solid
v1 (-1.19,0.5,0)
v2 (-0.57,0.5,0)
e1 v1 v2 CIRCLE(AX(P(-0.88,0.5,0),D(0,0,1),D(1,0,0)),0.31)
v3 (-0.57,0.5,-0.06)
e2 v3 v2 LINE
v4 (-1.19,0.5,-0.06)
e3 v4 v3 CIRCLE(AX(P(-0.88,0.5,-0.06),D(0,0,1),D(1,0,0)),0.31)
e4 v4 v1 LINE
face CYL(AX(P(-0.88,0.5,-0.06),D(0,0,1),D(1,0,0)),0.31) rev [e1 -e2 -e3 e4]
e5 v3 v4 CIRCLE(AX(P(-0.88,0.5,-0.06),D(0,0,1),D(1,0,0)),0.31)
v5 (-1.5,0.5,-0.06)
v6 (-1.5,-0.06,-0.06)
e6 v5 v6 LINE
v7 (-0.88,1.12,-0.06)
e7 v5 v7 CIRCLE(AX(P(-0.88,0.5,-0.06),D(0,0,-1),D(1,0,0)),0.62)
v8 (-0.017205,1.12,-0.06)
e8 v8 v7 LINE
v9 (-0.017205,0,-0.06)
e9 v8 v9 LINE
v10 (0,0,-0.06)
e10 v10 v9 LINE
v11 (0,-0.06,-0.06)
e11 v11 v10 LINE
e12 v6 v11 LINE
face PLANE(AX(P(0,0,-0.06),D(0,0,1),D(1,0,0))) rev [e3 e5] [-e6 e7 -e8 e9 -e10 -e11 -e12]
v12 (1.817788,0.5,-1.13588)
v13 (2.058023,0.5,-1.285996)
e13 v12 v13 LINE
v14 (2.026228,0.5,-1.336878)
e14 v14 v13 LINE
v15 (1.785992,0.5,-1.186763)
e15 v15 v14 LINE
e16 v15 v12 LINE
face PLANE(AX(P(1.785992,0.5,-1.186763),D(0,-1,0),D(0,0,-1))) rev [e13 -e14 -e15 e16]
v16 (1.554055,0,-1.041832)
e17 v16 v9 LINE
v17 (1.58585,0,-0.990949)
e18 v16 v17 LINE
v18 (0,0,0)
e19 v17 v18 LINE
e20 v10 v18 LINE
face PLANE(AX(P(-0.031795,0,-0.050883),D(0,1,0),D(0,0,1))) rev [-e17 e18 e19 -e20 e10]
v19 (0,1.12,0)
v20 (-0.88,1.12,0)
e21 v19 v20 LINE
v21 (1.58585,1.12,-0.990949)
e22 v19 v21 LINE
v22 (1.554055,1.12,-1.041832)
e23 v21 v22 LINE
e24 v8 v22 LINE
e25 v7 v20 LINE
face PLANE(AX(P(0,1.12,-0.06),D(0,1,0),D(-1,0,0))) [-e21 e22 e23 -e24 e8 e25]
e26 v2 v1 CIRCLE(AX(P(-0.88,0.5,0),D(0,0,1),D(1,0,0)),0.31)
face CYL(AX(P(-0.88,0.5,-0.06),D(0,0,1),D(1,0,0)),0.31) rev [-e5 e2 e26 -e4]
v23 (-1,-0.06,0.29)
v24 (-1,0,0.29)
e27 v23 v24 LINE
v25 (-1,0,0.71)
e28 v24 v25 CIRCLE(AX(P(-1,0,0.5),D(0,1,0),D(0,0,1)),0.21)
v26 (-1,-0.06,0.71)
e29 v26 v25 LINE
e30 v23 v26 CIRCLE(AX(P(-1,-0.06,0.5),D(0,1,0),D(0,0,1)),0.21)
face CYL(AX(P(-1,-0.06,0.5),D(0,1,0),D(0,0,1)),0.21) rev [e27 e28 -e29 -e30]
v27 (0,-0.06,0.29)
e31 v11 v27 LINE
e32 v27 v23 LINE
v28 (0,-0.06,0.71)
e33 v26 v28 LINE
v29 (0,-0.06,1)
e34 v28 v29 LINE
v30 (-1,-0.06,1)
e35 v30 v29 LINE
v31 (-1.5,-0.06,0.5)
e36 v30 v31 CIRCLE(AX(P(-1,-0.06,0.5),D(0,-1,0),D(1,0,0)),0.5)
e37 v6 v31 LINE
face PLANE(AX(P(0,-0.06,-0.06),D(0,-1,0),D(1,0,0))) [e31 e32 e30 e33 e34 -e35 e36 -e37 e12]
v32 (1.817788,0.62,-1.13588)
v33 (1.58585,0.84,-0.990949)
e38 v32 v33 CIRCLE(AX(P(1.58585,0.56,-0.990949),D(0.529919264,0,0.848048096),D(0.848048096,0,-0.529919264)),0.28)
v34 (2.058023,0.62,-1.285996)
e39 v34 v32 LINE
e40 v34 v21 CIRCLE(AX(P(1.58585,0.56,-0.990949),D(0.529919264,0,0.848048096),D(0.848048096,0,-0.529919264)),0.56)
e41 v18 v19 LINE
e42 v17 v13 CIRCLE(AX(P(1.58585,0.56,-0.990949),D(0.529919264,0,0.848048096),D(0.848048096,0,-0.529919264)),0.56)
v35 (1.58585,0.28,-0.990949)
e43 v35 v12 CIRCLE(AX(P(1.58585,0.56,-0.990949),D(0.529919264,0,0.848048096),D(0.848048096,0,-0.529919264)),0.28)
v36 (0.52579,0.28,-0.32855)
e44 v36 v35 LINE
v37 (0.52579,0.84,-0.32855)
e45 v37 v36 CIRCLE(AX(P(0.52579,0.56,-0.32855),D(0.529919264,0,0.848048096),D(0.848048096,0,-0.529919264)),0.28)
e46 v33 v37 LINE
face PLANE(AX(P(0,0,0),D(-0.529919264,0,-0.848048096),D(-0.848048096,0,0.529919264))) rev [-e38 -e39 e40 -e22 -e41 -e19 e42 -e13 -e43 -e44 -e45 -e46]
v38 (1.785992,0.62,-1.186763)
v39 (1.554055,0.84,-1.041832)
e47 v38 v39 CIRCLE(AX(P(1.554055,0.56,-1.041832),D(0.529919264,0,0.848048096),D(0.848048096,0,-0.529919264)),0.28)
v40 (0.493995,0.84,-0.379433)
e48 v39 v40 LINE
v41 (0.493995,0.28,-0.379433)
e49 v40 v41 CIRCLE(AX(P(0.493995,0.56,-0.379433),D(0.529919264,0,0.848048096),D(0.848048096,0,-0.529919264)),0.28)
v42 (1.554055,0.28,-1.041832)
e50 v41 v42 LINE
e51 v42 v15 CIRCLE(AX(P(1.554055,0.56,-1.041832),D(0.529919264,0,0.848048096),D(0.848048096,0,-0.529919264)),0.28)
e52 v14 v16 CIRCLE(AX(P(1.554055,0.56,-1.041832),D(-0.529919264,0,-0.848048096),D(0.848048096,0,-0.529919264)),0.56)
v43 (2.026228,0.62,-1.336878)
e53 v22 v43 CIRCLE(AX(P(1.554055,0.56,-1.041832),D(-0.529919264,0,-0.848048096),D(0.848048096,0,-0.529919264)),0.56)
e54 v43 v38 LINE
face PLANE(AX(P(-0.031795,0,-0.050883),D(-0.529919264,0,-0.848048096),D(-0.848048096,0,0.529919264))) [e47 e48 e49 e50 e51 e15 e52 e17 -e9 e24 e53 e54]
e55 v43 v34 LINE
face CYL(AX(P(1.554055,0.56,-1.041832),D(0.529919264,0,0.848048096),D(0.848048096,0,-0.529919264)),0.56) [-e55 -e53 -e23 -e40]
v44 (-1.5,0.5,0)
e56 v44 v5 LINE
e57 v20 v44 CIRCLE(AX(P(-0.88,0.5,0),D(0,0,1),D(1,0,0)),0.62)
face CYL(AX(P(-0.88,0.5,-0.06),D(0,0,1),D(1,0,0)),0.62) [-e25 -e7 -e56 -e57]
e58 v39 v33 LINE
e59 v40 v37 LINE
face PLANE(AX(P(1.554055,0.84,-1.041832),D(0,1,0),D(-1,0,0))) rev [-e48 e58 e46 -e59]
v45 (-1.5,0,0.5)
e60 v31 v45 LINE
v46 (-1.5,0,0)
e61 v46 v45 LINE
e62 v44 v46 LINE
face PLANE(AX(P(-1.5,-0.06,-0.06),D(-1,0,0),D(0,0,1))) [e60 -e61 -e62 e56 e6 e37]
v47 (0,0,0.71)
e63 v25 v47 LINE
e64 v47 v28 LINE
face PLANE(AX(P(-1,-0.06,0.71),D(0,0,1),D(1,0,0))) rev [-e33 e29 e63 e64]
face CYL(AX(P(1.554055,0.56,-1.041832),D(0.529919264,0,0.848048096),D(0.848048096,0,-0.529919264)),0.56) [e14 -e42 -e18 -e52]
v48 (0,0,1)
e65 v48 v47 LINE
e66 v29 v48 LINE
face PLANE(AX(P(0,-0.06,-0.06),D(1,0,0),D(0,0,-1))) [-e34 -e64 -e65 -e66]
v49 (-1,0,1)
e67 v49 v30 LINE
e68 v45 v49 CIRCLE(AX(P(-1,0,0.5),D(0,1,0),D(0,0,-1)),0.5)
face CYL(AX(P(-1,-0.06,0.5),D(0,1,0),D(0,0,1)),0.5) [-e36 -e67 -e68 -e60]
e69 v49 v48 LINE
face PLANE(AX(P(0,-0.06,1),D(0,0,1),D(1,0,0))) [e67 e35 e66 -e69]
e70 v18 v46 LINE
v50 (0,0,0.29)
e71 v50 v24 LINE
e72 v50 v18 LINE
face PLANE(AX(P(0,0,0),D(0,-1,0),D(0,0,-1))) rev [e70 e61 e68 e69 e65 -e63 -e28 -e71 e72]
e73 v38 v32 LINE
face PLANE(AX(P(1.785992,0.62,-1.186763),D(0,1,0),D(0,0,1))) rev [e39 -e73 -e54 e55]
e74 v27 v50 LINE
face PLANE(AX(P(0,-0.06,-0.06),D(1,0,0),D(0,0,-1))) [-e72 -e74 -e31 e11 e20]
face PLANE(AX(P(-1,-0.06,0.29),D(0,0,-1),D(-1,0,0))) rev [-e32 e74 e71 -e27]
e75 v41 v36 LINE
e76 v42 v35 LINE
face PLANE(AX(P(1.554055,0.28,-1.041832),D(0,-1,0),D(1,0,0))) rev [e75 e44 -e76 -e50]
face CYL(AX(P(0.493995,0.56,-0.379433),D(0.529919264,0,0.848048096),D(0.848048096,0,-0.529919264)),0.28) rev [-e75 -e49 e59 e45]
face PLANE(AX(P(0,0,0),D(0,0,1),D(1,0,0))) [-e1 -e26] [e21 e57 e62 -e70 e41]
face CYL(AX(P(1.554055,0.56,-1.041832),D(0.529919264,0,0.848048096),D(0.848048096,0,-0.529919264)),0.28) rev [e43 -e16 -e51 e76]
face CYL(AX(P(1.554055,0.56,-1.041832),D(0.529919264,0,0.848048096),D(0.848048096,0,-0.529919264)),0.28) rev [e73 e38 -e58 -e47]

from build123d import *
from OCP.BRepFilletAPI import BRepFilletAPI_MakeFillet

# Parameters (mm, degrees)
VERTICAL_TAB_SKETCH_W    = 1.5
VERTICAL_TAB_SKETCH_H    = 1.18
VERTICAL_TAB_DEPTH       = 0.06
FOOT_SKETCH_W            = 1.5
FOOT_SKETCH_H            = 1
FOOT_DEPTH               = 0.06
ARM_SKETCH_W             = 2.43
ARM_SKETCH_H             = 1.12
ANGLED_ARM_DEPTH         = 0.06
TAB_CORNER_ROUNDS_R1     = 0.62
TAB_CORNER_ROUNDS_R2     = 0.5
TAB_HOLE_SKETCH_R        = 0.31
TAB_HOLE_DEPTH           = 0.06
FOOT_OPEN_SLOT_DEPTH     = 0.06
ARM_END_ROUNDS_RADIUS    = 0.56
ARM_END_ROUNDS_LENGTH    = 0.06
ARM_SLOT_WITH_SLIT_DEPTH = 0.06


with BuildPart() as part:
    # Vertical Tab Sketch → Vertical Tab (new body)
    with BuildSketch(Plane.XY):
        with Locations((-0.75, 0.53)):
            Rectangle(VERTICAL_TAB_SKETCH_W, VERTICAL_TAB_SKETCH_H)
    extrude(amount=-VERTICAL_TAB_DEPTH)

    # Foot Sketch → Foot (add)
    with BuildSketch(Plane(origin=(0, 0, 0), x_dir=(1, 0, 0), z_dir=(0, 1, 0))):
        with Locations((-0.75, -0.5)):
            Rectangle(FOOT_SKETCH_W, FOOT_SKETCH_H)
    extrude(amount=-FOOT_DEPTH)

    # Arm Sketch → Angled Arm (add)
    with BuildSketch(Plane(origin=(0, 0, 0), x_dir=(0.8480480961564255, 0, -0.5299192642332059), z_dir=(-0.5299192642332058, 0, -0.8480480961564254))):
        with Locations((1.215, -0.56)):
            Rectangle(ARM_SKETCH_W, ARM_SKETCH_H)
    extrude(amount=ANGLED_ARM_DEPTH)

    # Tab Corner Rounds: one fillet with a radius per group of edges: ONE call of the kernel's fillet builder (fillet() takes one radius for all edges)
    tab_corner_rounds_edges_1 = [part.edges().sort_by_distance(p)[0] for p in [
        (-1.5, 1.12, -0.03),
    ]]
    tab_corner_rounds_edges_2 = [part.edges().sort_by_distance(p)[0] for p in [
        (-1.5, -0.03, 1),
    ]]
    tab_corner_rounds = BRepFilletAPI_MakeFillet(part.part.solid().wrapped)
    for e in tab_corner_rounds_edges_1:
        tab_corner_rounds.Add(TAB_CORNER_ROUNDS_R1, e.wrapped)
    for e in tab_corner_rounds_edges_2:
        tab_corner_rounds.Add(TAB_CORNER_ROUNDS_R2, e.wrapped)
    add(Compound.cast(tab_corner_rounds.Shape()), mode=Mode.REPLACE)

    # Tab Hole Sketch → Tab Hole (cut)
    with BuildSketch(Plane.XY):
        with Locations((-0.88, 0.5)):
            Circle(TAB_HOLE_SKETCH_R)
    extrude(amount=-TAB_HOLE_DEPTH, mode=Mode.SUBTRACT)

    # Foot Slot Sketch → Foot Open Slot (cut)
    with BuildSketch(Plane(origin=(0, 0, 0), x_dir=(1, 0, 0), z_dir=(0, 1, 0))):
        with BuildLine():
            Line((-1, -0.29), (0.146073604, -0.29))
            ThreePointArc((0.146073604, -0.29), (0.356073604, -0.5), (0.146073604, -0.71))
            Line((0.146073604, -0.71), (-1, -0.71))
            ThreePointArc((-1, -0.71), (-1.21, -0.5), (-1, -0.29))
        make_face()
    extrude(amount=-FOOT_OPEN_SLOT_DEPTH, mode=Mode.SUBTRACT)

    # Arm End Rounds: full round fillet: the end face becomes a half cylinder, R = half its width
    arm_end_rounds_face = Plane((2.044859296, 0.56, -1.313145255), x_dir=(0.529919264233, 0, 0.848048096156), z_dir=(0.848048096156, 0, -0.529919264233))  # on the end face: x along it, z out of the body
    arm_end_rounds_slab = arm_end_rounds_face.offset(-ARM_END_ROUNDS_RADIUS / 2) * Box(ARM_END_ROUNDS_LENGTH, 2 * ARM_END_ROUNDS_RADIUS, ARM_END_ROUNDS_RADIUS, mode=Mode.PRIVATE)  # the body's end, R deep
    arm_end_rounds_round = Plane((1.569952362, 0.56, -1.016390467), x_dir=(0.848048096156, 0, -0.529919264233), z_dir=(0.529919264233, 0, 0.848048096156)) * Cylinder(ARM_END_ROUNDS_RADIUS, ARM_END_ROUNDS_LENGTH, mode=Mode.PRIVATE)  # its axis R under the face
    add(arm_end_rounds_slab - arm_end_rounds_round, mode=Mode.SUBTRACT)

    # Arm Slot Sketch → Arm Slot with Slit (cut)
    with BuildSketch(Plane(origin=(0, 0, 0), x_dir=(0.8480480961564255, 0, -0.5299192642332059), z_dir=(0.5299192642332058, 0, 0.8480480961564254))):
        with BuildLine():
            Line((1.87, 0.28), (0.62, 0.28))
            ThreePointArc((0.62, 0.28), (0.34, 0.56), (0.62, 0.84))
            Line((0.62, 0.84), (1.87, 0.84))
            ThreePointArc((1.87, 0.84), (2.045499288, 0.778174242), (2.143495887, 0.62))
            Line((2.143495887, 0.62), (2.426776436, 0.62))
            Line((2.426776436, 0.62), (2.426776436, 0.5))
            Line((2.426776436, 0.5), (2.143495887, 0.5))
            ThreePointArc((2.143495887, 0.5), (2.045499288, 0.341825758), (1.87, 0.28))
        make_face()
    extrude(amount=-ARM_SLOT_WITH_SLIT_DEPTH, mode=Mode.SUBTRACT)


with BuildPart() as arm_slot_with_slit_kept_piece:
    # of the separate pieces the step leaves, the one the design keeps (arm_slot_with_slit_pieces_kept)
    add(part.part.solids().sort_by_distance((-1.5, -0.06, 0.5))[0])


solid = arm_slot_with_slit_kept_piece.part
